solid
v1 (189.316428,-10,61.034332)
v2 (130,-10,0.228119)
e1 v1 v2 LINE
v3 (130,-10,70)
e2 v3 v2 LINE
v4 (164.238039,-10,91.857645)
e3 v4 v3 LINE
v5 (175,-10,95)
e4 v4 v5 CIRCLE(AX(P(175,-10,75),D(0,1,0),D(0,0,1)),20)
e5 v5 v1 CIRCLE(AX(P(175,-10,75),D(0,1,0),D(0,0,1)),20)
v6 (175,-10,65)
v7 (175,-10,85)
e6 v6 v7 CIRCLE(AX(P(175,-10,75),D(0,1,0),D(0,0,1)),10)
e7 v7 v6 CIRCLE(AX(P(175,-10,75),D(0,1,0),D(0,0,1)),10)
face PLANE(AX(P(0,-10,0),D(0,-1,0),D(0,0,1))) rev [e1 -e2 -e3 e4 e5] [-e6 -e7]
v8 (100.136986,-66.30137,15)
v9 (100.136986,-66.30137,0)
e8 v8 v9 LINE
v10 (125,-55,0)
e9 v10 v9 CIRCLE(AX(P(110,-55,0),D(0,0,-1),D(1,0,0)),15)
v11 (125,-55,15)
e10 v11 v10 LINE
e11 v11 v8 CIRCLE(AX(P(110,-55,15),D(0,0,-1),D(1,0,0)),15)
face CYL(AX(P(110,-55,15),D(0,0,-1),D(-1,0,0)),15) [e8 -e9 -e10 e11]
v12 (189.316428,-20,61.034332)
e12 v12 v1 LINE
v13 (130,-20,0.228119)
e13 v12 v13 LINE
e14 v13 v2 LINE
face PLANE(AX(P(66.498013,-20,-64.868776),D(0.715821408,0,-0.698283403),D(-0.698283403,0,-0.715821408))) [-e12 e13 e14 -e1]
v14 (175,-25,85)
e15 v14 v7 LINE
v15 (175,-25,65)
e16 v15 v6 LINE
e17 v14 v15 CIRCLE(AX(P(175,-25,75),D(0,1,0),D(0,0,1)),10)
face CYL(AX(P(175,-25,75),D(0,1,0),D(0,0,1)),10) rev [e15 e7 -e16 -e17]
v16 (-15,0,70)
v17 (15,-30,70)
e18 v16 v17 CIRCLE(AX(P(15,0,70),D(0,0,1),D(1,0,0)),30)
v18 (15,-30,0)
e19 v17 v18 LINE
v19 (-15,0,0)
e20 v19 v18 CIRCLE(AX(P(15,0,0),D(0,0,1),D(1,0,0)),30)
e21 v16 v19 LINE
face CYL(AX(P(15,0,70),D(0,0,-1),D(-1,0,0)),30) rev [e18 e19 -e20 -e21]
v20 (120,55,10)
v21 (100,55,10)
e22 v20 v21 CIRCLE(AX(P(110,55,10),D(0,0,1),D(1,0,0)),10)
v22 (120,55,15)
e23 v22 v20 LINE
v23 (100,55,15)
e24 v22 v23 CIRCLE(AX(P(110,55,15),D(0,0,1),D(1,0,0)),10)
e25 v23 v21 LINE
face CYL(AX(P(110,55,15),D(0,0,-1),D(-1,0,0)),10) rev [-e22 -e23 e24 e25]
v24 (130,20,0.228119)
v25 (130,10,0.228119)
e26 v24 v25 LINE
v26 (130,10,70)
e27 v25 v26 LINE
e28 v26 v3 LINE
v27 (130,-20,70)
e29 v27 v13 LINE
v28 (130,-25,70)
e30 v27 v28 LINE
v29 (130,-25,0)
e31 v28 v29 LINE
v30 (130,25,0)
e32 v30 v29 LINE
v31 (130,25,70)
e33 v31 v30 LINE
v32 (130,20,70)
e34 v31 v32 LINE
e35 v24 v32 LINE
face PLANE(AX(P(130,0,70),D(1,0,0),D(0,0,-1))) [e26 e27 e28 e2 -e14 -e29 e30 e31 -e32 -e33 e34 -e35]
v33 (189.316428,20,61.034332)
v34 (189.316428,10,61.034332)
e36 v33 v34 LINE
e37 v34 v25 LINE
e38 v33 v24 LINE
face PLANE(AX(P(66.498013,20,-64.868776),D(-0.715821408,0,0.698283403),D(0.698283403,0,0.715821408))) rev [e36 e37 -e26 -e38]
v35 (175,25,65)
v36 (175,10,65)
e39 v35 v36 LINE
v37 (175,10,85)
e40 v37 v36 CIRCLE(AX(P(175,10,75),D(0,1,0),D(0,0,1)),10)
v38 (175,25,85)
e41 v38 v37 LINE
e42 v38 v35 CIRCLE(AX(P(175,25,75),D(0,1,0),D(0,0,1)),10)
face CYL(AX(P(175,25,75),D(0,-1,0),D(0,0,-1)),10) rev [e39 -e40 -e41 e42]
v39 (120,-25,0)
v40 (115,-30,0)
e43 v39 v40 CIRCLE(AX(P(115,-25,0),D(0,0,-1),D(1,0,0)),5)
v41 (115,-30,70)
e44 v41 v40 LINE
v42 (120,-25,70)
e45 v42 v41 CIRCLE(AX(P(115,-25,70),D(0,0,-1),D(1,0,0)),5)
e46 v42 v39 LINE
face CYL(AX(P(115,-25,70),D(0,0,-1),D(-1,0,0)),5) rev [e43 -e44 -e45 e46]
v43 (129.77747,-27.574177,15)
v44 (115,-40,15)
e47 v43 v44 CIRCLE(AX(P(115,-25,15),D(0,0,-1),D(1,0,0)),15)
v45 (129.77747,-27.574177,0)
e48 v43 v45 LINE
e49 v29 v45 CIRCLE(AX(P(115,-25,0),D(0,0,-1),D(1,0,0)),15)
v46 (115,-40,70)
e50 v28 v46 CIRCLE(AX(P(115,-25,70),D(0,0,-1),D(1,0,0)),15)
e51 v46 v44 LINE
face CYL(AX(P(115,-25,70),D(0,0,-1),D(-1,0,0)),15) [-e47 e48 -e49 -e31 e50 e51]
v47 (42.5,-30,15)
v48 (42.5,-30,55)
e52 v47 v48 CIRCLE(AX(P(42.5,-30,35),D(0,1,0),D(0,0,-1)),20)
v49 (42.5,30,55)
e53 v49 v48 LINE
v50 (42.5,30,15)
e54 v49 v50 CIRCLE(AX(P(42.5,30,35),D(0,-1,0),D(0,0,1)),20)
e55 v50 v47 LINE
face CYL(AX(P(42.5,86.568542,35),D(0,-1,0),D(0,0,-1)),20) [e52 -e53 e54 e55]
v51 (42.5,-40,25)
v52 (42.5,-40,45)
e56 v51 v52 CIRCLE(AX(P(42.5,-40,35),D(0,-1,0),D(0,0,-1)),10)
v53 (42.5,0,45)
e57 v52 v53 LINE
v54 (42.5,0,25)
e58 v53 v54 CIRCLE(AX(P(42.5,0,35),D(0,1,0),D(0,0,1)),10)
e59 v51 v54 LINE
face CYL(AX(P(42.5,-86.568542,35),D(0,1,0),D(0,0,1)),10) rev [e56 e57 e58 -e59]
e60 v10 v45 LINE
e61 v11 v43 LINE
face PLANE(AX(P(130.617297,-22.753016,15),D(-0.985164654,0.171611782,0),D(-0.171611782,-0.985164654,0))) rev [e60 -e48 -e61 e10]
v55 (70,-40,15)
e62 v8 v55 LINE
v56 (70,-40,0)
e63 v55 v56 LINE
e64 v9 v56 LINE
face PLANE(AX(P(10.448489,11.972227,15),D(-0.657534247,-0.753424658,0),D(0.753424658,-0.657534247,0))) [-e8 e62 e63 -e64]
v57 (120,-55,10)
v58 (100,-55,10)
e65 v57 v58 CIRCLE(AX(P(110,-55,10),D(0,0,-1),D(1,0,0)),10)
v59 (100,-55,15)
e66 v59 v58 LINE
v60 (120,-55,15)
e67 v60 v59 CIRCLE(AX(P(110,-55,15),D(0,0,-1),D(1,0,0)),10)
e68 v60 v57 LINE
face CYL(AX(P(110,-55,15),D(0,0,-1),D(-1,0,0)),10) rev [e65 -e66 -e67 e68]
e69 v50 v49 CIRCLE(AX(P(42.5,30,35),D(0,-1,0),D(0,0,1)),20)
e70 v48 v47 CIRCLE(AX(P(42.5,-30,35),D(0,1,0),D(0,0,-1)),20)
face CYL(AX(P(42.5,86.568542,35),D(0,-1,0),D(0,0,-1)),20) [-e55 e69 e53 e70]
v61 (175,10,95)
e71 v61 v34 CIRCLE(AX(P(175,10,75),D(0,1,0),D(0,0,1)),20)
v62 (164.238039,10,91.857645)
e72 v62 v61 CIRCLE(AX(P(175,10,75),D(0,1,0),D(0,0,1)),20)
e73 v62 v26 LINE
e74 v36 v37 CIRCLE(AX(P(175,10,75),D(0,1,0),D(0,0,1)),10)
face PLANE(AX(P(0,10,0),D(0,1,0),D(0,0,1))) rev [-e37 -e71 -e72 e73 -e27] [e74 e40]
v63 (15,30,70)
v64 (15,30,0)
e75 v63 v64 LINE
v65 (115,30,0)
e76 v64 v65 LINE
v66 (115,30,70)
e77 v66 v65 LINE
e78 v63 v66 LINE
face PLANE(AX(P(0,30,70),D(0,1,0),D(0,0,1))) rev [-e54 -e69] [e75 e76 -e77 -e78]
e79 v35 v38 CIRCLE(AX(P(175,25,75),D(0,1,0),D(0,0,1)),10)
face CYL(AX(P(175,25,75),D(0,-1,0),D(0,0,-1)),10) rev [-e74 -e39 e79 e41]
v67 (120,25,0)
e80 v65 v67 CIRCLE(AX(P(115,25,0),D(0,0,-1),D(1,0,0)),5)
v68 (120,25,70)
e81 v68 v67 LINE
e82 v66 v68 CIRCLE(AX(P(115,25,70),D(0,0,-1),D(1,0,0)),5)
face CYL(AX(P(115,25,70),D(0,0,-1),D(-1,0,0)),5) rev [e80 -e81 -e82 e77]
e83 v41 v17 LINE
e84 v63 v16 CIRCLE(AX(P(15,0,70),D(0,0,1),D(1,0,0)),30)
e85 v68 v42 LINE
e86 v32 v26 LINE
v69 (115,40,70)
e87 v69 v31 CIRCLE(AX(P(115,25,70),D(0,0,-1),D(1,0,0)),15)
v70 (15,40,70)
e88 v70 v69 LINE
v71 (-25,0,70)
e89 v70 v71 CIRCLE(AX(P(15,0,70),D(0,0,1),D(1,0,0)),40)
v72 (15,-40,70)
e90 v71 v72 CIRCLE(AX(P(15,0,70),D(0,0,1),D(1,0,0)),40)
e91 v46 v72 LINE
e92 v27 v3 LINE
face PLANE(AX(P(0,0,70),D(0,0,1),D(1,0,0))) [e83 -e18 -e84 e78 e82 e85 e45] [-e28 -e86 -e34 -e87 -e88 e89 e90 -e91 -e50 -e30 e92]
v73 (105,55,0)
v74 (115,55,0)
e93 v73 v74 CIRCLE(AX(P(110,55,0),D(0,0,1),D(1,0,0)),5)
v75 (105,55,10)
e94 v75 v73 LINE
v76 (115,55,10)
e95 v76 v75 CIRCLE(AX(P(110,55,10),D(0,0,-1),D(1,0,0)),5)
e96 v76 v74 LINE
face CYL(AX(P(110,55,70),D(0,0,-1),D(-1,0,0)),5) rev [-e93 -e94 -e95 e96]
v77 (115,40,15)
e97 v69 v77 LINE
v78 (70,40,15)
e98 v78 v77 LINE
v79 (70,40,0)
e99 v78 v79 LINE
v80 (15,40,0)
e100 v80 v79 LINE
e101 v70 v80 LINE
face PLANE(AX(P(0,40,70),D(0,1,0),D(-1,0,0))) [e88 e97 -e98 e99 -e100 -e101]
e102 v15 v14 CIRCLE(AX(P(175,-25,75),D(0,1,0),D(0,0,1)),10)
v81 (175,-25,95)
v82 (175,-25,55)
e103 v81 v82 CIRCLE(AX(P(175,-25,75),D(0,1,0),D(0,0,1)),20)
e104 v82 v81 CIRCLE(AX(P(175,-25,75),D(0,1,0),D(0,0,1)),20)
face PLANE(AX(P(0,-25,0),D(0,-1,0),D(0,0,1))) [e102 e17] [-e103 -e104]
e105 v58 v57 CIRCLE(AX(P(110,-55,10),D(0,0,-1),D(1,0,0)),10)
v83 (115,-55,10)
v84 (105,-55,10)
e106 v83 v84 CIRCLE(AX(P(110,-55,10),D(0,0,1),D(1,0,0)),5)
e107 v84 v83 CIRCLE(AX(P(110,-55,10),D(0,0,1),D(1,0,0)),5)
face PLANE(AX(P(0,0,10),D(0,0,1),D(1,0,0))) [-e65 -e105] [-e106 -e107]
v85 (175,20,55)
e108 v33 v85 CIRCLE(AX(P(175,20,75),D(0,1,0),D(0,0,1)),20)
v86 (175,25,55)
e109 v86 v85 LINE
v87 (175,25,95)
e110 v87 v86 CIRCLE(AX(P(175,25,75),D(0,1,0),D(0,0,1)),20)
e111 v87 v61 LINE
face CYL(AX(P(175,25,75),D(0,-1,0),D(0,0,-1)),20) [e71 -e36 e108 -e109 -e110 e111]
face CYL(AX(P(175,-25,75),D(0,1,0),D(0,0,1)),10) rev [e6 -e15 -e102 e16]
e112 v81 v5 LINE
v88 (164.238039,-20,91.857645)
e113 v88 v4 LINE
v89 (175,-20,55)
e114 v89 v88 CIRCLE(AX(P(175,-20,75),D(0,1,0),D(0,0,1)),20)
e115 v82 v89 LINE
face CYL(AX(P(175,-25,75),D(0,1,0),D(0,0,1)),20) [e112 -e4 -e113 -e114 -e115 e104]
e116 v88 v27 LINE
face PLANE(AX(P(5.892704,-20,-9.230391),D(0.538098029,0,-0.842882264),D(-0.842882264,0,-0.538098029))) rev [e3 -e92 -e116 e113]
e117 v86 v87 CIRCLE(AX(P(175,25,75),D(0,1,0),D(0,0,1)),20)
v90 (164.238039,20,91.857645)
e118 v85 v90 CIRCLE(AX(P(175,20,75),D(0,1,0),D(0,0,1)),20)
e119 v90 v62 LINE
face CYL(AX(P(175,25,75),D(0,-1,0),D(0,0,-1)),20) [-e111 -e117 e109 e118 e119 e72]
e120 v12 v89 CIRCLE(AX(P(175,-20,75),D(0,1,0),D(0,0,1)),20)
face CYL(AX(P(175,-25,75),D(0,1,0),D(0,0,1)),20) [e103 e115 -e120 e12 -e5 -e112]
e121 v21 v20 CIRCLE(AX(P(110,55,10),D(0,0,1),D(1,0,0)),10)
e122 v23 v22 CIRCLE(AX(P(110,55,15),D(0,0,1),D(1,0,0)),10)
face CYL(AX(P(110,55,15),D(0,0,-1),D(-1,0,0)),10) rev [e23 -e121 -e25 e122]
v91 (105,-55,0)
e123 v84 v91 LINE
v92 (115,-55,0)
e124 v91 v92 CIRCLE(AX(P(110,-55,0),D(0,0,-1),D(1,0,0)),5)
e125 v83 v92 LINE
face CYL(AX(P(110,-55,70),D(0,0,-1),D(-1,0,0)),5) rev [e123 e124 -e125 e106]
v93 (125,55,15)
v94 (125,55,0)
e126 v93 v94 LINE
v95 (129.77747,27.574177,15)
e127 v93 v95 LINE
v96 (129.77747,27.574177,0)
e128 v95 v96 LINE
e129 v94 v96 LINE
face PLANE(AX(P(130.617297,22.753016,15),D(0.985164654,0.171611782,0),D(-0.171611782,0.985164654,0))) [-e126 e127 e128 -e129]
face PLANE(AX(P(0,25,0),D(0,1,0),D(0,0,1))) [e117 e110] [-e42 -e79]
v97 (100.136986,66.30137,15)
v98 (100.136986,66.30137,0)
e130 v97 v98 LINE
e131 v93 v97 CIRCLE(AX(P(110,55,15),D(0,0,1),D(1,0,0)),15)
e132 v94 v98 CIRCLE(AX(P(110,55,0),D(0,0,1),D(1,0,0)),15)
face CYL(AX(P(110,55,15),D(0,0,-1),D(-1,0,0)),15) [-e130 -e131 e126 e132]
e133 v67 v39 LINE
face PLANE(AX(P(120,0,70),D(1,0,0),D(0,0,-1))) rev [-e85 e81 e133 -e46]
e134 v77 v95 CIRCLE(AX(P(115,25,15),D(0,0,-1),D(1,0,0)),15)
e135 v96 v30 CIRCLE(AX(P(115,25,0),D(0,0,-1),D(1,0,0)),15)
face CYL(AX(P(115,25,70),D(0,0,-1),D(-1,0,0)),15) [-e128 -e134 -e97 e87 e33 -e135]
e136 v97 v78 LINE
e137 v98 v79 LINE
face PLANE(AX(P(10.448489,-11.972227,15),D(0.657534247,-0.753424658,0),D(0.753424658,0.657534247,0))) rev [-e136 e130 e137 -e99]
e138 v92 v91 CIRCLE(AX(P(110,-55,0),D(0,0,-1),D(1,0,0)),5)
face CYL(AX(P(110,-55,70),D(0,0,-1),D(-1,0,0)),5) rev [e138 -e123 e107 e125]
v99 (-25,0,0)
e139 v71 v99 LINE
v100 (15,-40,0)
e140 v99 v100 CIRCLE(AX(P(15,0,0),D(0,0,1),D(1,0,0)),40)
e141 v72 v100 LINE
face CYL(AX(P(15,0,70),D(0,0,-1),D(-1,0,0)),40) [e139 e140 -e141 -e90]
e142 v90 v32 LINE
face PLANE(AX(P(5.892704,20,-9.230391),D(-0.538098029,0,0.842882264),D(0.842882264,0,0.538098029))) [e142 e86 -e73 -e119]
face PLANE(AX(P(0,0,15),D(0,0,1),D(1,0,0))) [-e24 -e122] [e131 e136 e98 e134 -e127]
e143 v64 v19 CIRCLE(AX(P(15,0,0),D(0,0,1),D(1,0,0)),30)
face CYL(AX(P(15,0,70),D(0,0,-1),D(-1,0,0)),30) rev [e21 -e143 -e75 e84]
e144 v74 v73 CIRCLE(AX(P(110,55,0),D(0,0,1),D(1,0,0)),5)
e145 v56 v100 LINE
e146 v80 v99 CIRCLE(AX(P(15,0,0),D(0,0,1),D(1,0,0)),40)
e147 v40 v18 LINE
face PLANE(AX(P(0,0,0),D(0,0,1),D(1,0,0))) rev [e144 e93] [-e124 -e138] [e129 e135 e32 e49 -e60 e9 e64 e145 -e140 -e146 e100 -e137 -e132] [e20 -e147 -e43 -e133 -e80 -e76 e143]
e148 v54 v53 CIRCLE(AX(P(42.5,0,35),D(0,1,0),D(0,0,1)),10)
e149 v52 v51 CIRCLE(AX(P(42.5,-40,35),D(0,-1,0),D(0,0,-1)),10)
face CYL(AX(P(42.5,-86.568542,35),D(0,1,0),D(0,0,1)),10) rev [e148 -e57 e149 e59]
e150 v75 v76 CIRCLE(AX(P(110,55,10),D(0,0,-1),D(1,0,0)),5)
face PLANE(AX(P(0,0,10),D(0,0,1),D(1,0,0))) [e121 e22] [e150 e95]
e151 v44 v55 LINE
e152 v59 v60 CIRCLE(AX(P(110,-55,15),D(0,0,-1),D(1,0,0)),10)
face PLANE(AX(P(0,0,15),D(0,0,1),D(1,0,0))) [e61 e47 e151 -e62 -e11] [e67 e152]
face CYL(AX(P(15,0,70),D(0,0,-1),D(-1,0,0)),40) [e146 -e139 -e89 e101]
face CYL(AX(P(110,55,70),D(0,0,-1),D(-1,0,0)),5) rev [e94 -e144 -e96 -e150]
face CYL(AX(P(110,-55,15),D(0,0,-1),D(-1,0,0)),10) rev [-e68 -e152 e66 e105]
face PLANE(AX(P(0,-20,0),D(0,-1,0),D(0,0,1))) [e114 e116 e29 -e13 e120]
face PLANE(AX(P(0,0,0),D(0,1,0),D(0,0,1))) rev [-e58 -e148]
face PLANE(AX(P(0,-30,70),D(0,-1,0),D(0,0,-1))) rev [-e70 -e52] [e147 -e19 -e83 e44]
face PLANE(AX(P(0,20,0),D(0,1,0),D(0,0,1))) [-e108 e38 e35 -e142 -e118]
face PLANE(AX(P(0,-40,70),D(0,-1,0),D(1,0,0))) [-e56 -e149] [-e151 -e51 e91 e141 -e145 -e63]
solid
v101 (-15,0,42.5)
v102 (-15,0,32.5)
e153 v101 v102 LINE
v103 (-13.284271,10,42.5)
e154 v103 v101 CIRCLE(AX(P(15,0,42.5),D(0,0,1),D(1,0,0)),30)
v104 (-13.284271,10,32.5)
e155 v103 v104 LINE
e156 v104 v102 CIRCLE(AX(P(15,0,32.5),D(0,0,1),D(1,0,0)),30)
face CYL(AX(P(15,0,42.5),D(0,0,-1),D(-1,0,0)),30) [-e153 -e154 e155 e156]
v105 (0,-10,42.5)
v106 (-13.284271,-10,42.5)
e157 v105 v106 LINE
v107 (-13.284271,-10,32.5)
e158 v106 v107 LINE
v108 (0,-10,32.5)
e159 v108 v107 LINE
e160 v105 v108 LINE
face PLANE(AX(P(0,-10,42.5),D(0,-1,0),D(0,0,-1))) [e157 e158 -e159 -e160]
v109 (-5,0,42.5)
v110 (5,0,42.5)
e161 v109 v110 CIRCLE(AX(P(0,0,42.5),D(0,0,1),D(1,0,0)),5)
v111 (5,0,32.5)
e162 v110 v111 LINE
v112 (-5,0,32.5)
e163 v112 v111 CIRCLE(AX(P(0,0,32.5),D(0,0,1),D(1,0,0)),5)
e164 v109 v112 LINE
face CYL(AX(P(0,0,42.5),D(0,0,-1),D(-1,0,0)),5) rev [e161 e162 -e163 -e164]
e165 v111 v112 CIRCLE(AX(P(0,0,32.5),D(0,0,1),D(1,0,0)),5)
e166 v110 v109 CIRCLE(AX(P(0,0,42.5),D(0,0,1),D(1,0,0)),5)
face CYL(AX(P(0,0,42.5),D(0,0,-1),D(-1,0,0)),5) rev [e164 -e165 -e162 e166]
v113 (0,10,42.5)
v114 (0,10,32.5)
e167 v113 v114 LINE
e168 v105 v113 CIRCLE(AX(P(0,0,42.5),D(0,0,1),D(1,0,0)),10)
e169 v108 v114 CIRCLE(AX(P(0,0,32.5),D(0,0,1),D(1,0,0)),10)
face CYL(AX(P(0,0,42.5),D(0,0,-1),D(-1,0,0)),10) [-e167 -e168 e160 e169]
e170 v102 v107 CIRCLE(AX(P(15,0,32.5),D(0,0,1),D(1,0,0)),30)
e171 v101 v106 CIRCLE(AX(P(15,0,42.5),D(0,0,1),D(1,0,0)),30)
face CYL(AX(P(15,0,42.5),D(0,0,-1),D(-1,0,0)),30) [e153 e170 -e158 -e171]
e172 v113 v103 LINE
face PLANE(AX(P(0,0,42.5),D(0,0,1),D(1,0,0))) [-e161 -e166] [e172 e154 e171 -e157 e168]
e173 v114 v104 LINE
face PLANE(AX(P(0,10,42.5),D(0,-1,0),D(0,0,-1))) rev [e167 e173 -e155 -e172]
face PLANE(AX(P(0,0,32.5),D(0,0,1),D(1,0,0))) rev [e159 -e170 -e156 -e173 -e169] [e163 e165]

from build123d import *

# Parameters (mm, degrees)
HOUSING_SHELL_70MM_DEPTH      = 70
SKETCH1_3_R                   = 10
SKETCH1_3_R_2                 = 5
FRONT_LUG_BOSS_15MM_DEPTH     = 15
FRONT_START                   = 10
SKETCH1_6_R                   = 10
SKETCH1_6_R_2                 = 5
FRONT_LUG_CUT_5MM_DEPTH       = 5
SKETCH1_7_R                   = 5
FRONT_PROFILE_CUT_DEPTH       = 164.401346384
TOP_PROFILE_SKETCH_R          = 20
TOP_PROFILE_SKETCH_R_2        = 10
TOP_BOSS_PRIMARY_DEPTH        = 30
TOP_START                     = -30
SKETCH2_3_R                   = 20
SKETCH2_3_R_2                 = 10
TOP_BOSS_SECONDARY_DEPTH      = 30
TOP_START_2                   = -40
SKETCH2_4_R                   = 10
TOP_CUT_10MM_DEPTH            = 10
EAR_START                     = 10
EAR_BOSS_10MM_DEPTH           = 10
SKETCH4_3_R                   = 20
SKETCH4_3_R_2                 = 10
EAR_BOSS_15MM_DEPTH           = 15
SEPARATE_START                = 32.5
SKETCH1_8_R                   = 5
SEPARATE_BOSS_BODY_10MM_DEPTH = 10


with BuildPart() as part:
    # Front Profile Sketch → Housing Shell 70mm (new body)
    with BuildSketch(Plane.XY):
        with BuildLine():
            ThreePointArc((115, 40), (125.606601718, 35.606601718), (130, 25))
            Line((130, 25), (130, -25))
            ThreePointArc((130, -25), (125.606601718, -35.606601718), (115, -40))
            Line((115, -40), (15, -40))
            ThreePointArc((15, -40), (-25, 0), (15, 40))
            Line((15, 40), (115, 40))
        make_face()
        with BuildLine():
            ThreePointArc((15, 30), (-15, 0), (15, -30))
            Line((15, -30), (115, -30))
            ThreePointArc((115, -30), (118.535533906, -28.535533906), (120, -25))
            Line((120, -25), (120, 25))
            ThreePointArc((120, 25), (118.535533906, 28.535533906), (115, 30))
            Line((115, 30), (15, 30))
        make_face(mode=Mode.SUBTRACT)
    extrude(amount=HOUSING_SHELL_70MM_DEPTH)

    # Sketch1_3 → Front Lug Boss 15mm (add)
    # profile 1 of 6: a face of its own
    with BuildSketch(Plane.XY):
        with BuildLine():
            Line((100.136986301, 66.301369863), (70, 40))
            Line((70, 40), (115, 40))
            ThreePointArc((115, 40), (124.653687096, 36.480693597), (129.777469816, 27.574176728))
            Line((129.777469816, 27.574176728), (125, 55))
            ThreePointArc((125, 55), (116.207044165, 68.655497162), (100.136986301, 66.301369863))
        make_face()
        with Locations((110, 55)):
            Circle(SKETCH1_3_R, mode=Mode.SUBTRACT)
    # profile 2 of 6: a face of its own
    with BuildSketch(Plane.XY):
        with Locations((110, 55)):
            Circle(SKETCH1_3_R)
        with Locations((110, 55)):
            Circle(SKETCH1_3_R_2, mode=Mode.SUBTRACT)
    # profile 3 of 6: a face of its own
    with BuildSketch(Plane.XY):
        with Locations((110, 55)):
            Circle(SKETCH1_3_R_2)
    # profile 4 of 6: a face of its own
    with BuildSketch(Plane.XY):
        with BuildLine():
            Line((115, -40), (70, -40))
            Line((70, -40), (100.136986301, -66.301369863))
            ThreePointArc((100.136986301, -66.301369863), (116.207044165, -68.655497162), (125, -55))
            Line((125, -55), (129.777469816, -27.574176728))
            ThreePointArc((129.777469816, -27.574176728), (124.653687096, -36.480693597), (115, -40))
        make_face()
        with Locations((110, -55)):
            Circle(SKETCH1_3_R, mode=Mode.SUBTRACT)
    # profile 5 of 6: a face of its own
    with BuildSketch(Plane.XY):
        with Locations((110, -55)):
            Circle(SKETCH1_3_R)
        with Locations((110, -55)):
            Circle(SKETCH1_3_R_2, mode=Mode.SUBTRACT)
    # profile 6 of 6: a face of its own
    with BuildSketch(Plane.XY):
        with Locations((110, -55)):
            Circle(SKETCH1_3_R_2)
    extrude(amount=FRONT_LUG_BOSS_15MM_DEPTH)

    # Sketch1_6 → Front Lug Cut 5mm (cut)
    # profile 1 of 4: a face of its own
    with BuildSketch(Plane.XY.offset(FRONT_START)):
        with Locations((110, -55)):
            Circle(SKETCH1_6_R)
        with Locations((110, -55)):
            Circle(SKETCH1_6_R_2, mode=Mode.SUBTRACT)
    # profile 2 of 4: a face of its own
    with BuildSketch(Plane.XY.offset(FRONT_START)):
        with Locations((110, -55)):
            Circle(SKETCH1_6_R_2)
    # profile 3 of 4: a face of its own
    with BuildSketch(Plane.XY.offset(FRONT_START)):
        with Locations((110, 55)):
            Circle(SKETCH1_6_R)
        with Locations((110, 55)):
            Circle(SKETCH1_6_R_2, mode=Mode.SUBTRACT)
    # profile 4 of 4: a face of its own
    with BuildSketch(Plane.XY.offset(FRONT_START)):
        with Locations((110, 55)):
            Circle(SKETCH1_6_R_2)
    extrude(amount=FRONT_LUG_CUT_5MM_DEPTH, mode=Mode.SUBTRACT)

    # Sketch1_7 → Front Profile Cut (cut, through all)
    with BuildSketch(Plane.XY):
        with Locations((110, 55)):
            Circle(SKETCH1_7_R)
        with Locations((110, -55)):
            Circle(SKETCH1_7_R)
    extrude(amount=FRONT_PROFILE_CUT_DEPTH, mode=Mode.SUBTRACT)

    # Top Profile Sketch → Top Boss Primary (add)
    # profile 1 of 2: a face of its own
    with BuildSketch(Plane(origin=(0, 0, 0), x_dir=(1, 0, 0), z_dir=(0, 1, 0))):
        with Locations(Location((42.5, -35, 0), (0, 0, 270))):
            Circle(TOP_PROFILE_SKETCH_R)
        with Locations((42.5, -35)):
            Circle(TOP_PROFILE_SKETCH_R_2, mode=Mode.SUBTRACT)
    # profile 2 of 2: a face of its own
    with BuildSketch(Plane(origin=(0, 0, 0), x_dir=(1, 0, 0), z_dir=(0, 1, 0))):
        with Locations((42.5, -35)):
            Circle(TOP_PROFILE_SKETCH_R_2)
    extrude(amount=TOP_BOSS_PRIMARY_DEPTH)

    # Sketch2_3 → Top Boss Secondary (add)
    with BuildSketch(Plane(origin=(0, 0, 0), x_dir=(1, 0, 0), z_dir=(0, 1, 0)).offset(TOP_START)):
        with Locations(Location((42.5, -35, 0), (0, 0, 90))):
            Circle(SKETCH2_3_R)
        with Locations(Location((42.5, -35, 0), (0, 0, 270))):
            Circle(SKETCH2_3_R_2, mode=Mode.SUBTRACT)
    extrude(amount=TOP_BOSS_SECONDARY_DEPTH)

    # Sketch2_4 → Top Cut 10mm (cut)
    with BuildSketch(Plane(origin=(0, 0, 0), x_dir=(1, 0, 0), z_dir=(0, 1, 0)).offset(TOP_START_2)):
        with Locations(Location((42.5, -35, 0), (0, 0, 270))):
            Circle(SKETCH2_4_R)
    extrude(amount=TOP_CUT_10MM_DEPTH, mode=Mode.SUBTRACT)

    # Ear Profile Sketch → Ear Boss 10mm (add)
    with BuildSketch(Plane(origin=(0, 0, 0), x_dir=(1, 0, 0), z_dir=(0, 1, 0)).offset(EAR_START)):
        with BuildLine():
            Line((130, -70), (164.238039414, -91.857645278))
            ThreePointArc((164.238039414, -91.857645278), (159.486208673, -62.377707075), (189.316428168, -61.034331934))
            Line((189.316428168, -61.034331934), (129.777469816, 0))
            Line((129.777469816, 0), (130, -70))
        make_face()
    ear_boss_10mm = extrude(amount=EAR_BOSS_10MM_DEPTH)

    # Sketch4_3 → Ear Boss 15mm (add)
    with BuildSketch(Plane(origin=(0, 0, 0), x_dir=(1, 0, 0), z_dir=(0, 1, 0)).offset(EAR_START)):
        with Locations(Location((175, -75, 0), (0, 0, 44.28944294))):
            Circle(SKETCH4_3_R)
        with Locations(Location((175, -75, 0), (0, 0, 270))):
            Circle(SKETCH4_3_R_2, mode=Mode.SUBTRACT)
    ear_boss_15mm = extrude(amount=EAR_BOSS_15MM_DEPTH)

    # Ear Bosses Mirror: Ear Boss 10mm, Ear Boss 15mm across plane
    add(ear_boss_10mm.mirror(Plane.ZX))
    add(ear_boss_15mm.mirror(Plane.ZX))


with BuildPart() as body_2:
    # Sketch1_8 → Separate Boss Body 10mm (new body)
    with BuildSketch(Plane.XY.offset(SEPARATE_START)):
        with BuildLine():
            Line((0, 10), (-13.284271247, 10))
            ThreePointArc((-13.284271247, 10), (-15, 0), (-13.284271247, -10))
            Line((-13.284271247, -10), (0, -10))
            ThreePointArc((0, -10), (10, 0), (0, 10))
        make_face()
        Circle(SKETCH1_8_R, mode=Mode.SUBTRACT)
    extrude(amount=SEPARATE_BOSS_BODY_10MM_DEPTH)


solid = Compound([part.part, body_2.part])
